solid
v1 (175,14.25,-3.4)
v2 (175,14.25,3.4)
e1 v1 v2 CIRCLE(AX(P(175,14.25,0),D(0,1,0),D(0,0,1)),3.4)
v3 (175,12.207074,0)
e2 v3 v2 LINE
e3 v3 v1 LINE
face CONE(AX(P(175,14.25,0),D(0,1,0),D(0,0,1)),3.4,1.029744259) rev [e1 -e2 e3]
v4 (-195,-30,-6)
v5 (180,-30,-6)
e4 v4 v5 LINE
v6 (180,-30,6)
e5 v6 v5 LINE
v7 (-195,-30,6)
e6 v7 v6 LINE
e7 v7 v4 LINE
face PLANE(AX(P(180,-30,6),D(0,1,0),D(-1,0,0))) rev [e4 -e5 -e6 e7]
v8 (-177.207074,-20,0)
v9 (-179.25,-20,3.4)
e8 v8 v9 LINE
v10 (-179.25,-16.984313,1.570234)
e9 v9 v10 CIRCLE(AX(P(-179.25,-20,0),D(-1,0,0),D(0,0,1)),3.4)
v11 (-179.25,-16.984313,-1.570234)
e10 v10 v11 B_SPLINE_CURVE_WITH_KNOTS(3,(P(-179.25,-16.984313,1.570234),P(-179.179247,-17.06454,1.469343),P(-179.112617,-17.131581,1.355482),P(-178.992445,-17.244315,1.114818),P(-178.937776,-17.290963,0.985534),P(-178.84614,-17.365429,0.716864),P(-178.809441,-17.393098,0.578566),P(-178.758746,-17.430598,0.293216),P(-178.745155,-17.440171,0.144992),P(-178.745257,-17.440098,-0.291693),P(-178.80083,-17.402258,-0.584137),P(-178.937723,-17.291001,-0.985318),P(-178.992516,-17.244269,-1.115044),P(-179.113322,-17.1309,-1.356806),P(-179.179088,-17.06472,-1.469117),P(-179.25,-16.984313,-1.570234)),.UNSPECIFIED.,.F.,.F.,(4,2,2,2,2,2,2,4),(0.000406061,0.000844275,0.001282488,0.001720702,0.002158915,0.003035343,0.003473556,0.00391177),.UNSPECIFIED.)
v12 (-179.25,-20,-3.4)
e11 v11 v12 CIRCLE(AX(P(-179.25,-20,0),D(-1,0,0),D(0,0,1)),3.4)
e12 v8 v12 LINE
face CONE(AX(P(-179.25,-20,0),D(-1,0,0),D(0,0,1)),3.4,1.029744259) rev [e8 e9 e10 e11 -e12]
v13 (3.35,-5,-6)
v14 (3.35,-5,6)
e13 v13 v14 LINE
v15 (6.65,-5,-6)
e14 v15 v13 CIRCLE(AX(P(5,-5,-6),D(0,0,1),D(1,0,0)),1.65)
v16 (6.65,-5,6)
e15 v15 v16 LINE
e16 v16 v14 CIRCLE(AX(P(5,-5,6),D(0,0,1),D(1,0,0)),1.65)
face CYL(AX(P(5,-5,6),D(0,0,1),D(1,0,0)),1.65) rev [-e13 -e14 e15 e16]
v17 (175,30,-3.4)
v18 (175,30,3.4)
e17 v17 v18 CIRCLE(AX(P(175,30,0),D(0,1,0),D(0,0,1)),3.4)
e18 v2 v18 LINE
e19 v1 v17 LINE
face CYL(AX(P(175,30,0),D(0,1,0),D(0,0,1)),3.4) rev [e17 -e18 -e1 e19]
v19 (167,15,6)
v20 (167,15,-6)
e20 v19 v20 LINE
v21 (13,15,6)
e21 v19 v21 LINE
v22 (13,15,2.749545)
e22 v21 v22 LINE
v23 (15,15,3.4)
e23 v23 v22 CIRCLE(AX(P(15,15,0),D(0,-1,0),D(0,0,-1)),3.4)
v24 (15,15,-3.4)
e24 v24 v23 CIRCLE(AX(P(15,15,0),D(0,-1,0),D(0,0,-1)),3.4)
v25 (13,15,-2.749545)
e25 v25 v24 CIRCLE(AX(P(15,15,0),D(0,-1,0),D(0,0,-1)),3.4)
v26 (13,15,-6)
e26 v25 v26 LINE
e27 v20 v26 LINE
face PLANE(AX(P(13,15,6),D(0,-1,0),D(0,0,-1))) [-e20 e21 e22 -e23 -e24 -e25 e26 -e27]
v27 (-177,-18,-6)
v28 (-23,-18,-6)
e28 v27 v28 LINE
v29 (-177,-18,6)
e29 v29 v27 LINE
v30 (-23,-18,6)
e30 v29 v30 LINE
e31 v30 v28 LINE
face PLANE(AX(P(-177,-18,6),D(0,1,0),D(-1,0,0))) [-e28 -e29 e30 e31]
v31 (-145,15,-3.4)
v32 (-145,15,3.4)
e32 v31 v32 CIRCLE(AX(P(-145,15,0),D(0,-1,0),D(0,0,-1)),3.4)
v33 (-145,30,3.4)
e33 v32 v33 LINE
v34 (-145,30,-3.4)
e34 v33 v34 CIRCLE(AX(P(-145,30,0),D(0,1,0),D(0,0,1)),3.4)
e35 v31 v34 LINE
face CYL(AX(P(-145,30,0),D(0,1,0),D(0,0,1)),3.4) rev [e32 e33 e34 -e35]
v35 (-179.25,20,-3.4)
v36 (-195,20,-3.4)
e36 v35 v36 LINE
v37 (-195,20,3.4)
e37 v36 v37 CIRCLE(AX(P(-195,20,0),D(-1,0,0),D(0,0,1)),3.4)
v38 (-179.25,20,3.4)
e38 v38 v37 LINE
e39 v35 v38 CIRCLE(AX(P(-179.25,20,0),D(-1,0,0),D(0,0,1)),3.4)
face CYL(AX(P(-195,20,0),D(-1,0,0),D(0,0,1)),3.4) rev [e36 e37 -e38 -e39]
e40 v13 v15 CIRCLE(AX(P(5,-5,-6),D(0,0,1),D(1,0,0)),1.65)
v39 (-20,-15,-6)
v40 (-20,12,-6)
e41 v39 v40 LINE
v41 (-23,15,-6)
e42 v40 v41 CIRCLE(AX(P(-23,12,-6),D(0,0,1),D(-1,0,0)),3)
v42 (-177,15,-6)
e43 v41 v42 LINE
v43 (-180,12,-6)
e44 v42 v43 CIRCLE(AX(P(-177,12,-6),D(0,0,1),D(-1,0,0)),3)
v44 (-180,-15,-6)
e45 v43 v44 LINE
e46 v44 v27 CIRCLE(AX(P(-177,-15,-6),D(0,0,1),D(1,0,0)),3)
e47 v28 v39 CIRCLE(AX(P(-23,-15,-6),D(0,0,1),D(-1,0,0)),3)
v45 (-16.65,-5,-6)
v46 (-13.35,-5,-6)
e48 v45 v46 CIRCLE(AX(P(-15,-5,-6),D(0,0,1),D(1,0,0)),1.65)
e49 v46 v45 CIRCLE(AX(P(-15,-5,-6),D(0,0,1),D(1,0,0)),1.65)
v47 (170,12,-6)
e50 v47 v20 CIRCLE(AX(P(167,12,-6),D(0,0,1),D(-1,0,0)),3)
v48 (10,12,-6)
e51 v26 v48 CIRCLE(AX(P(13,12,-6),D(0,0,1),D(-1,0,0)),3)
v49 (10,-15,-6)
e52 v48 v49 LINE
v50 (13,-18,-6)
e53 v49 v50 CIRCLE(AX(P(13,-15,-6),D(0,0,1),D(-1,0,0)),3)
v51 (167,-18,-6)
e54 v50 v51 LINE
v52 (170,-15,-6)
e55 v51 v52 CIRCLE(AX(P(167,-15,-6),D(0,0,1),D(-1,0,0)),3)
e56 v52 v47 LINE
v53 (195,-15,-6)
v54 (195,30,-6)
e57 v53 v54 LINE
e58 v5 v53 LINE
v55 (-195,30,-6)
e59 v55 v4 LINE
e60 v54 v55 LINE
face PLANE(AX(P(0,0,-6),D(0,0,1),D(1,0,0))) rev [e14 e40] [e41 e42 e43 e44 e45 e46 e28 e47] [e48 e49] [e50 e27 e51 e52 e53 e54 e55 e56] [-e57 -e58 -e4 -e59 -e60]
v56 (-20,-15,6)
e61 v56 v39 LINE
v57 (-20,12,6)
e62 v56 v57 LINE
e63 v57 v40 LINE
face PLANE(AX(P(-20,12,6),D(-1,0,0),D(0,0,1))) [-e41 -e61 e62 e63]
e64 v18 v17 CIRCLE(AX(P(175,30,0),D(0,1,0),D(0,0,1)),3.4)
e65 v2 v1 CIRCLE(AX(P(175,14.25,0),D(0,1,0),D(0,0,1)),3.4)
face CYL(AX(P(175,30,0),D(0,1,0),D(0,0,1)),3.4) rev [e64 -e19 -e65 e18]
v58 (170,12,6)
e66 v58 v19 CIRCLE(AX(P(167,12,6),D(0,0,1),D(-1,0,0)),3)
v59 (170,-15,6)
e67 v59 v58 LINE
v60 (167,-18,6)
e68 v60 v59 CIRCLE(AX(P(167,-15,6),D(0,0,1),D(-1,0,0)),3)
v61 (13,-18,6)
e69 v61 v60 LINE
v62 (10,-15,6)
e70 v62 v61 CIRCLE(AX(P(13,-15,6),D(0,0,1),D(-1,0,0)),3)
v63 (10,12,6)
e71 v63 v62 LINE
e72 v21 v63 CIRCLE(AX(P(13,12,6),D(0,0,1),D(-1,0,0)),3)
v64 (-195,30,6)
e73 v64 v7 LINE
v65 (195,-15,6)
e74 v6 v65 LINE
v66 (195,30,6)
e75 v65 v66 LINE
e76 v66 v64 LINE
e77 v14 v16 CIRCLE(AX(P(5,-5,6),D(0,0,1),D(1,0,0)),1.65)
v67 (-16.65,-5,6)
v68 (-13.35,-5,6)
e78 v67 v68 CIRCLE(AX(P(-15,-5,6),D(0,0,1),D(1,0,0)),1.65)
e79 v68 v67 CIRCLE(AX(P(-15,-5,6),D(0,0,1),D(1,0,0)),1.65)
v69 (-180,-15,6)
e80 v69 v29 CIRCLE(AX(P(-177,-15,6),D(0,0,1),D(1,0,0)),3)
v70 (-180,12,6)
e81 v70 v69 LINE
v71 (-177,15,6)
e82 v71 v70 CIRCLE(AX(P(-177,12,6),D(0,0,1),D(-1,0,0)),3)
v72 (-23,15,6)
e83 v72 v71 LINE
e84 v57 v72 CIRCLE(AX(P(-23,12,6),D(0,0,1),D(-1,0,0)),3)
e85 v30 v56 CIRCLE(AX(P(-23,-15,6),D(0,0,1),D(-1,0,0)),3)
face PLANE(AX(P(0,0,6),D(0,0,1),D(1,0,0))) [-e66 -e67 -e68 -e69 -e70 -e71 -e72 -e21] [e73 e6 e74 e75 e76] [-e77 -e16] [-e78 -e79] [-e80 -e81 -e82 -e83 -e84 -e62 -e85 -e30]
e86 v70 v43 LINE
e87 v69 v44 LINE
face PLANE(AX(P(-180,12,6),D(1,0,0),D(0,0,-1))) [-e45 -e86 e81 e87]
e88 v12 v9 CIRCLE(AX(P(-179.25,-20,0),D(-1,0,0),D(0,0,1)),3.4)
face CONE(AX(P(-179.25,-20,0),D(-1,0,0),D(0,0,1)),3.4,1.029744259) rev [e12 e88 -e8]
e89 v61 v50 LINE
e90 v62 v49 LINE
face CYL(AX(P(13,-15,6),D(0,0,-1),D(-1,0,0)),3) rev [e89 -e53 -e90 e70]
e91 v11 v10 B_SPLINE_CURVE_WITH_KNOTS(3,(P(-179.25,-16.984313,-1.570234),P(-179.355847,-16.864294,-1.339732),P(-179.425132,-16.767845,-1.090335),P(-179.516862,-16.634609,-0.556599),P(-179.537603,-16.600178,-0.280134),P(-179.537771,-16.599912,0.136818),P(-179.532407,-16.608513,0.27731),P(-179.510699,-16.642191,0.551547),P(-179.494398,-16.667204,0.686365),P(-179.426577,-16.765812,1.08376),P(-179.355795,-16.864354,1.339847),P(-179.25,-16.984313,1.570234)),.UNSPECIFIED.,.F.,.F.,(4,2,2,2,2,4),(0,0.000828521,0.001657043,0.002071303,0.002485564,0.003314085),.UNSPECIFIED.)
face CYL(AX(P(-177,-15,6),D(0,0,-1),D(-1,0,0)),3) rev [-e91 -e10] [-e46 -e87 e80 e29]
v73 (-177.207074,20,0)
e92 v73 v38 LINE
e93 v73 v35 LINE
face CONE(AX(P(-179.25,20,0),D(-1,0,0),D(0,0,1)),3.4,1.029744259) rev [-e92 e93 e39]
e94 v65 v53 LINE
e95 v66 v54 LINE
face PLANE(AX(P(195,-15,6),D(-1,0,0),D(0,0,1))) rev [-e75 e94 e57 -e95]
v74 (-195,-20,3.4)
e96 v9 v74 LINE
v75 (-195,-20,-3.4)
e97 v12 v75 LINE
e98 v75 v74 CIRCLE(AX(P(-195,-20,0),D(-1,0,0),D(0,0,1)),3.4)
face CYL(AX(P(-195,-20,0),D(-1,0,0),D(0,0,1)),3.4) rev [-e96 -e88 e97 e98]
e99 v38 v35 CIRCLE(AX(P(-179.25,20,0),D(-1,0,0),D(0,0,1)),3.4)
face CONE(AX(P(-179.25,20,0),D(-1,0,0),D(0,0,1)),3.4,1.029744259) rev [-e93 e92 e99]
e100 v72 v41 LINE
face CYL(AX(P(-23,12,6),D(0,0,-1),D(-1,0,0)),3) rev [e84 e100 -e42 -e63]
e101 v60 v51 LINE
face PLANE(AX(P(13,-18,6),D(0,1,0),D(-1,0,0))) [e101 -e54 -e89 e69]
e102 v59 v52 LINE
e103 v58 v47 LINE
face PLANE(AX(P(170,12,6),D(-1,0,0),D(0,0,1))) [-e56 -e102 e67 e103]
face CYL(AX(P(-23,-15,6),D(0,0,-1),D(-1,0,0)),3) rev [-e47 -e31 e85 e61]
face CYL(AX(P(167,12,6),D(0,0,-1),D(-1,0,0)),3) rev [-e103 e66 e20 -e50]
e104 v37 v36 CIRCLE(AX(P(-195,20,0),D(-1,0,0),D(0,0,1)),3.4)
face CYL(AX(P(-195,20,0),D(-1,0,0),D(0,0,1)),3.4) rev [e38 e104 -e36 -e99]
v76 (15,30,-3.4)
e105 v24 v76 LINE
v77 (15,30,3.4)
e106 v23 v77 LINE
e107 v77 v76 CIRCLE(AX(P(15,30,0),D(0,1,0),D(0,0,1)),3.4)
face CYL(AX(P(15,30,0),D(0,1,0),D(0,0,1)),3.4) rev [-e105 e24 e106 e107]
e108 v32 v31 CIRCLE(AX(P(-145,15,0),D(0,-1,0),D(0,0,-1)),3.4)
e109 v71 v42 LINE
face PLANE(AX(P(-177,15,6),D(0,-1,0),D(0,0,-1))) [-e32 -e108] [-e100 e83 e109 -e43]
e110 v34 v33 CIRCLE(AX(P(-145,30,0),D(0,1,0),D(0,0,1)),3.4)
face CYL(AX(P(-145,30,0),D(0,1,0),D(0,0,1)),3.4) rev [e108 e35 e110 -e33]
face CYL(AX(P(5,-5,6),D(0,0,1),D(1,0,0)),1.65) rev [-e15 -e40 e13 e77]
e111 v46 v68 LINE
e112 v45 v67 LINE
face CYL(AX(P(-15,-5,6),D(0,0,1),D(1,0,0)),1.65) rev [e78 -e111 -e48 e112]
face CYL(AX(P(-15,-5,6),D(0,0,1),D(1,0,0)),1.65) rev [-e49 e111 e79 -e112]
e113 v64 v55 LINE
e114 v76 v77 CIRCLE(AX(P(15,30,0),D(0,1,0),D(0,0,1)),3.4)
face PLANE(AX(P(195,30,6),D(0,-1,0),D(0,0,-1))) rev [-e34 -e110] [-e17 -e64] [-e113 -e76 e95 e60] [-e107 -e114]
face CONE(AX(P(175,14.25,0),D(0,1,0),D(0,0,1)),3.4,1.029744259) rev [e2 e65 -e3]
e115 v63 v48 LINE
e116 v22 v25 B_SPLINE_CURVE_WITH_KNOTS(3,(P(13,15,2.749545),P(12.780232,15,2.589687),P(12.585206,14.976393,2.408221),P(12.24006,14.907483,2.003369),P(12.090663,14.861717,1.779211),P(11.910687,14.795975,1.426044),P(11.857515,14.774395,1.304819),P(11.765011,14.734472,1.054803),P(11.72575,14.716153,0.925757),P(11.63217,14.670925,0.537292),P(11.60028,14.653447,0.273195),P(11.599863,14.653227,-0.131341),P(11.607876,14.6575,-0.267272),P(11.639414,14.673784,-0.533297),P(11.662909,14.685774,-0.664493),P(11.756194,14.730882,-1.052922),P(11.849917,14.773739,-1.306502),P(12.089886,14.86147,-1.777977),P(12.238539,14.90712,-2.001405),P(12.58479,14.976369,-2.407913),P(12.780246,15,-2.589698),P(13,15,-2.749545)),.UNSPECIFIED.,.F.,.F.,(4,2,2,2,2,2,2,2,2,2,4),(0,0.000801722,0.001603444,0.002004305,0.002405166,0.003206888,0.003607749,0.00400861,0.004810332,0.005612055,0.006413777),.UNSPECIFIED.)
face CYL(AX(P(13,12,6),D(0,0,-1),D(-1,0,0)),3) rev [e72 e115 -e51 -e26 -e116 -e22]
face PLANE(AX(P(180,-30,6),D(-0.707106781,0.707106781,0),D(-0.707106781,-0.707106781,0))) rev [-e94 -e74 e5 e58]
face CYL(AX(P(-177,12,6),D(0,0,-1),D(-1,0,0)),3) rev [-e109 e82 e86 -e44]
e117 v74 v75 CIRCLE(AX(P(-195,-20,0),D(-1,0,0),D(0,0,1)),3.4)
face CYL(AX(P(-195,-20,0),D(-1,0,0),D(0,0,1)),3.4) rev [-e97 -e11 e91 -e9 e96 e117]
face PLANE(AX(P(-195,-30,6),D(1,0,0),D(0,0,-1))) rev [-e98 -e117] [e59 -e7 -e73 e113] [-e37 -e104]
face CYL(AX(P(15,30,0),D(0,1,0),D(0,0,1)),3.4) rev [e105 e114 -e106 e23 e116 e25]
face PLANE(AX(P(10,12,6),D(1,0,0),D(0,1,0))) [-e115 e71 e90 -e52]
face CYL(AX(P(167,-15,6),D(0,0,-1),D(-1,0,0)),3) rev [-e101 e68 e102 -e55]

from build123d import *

# Parameters (mm, degrees)
EXTRUDE_1_DEPTH        = 6
HOLE_WIZARD_M8_1_D     = 6.8
HOLE_WIZARD_M8_1_DEPTH = 15.75
HOLE_WIZARD_M8_1_TIP   = 2.042926105
HOLE_WIZARD_M4_1_D     = 3.3
PATTERN_LINEAR_1_COUNT = 3
PATTERN_LINEAR_1_PITCH = 160


with BuildPart() as part:
    # 草图1 → 凸台-拉伸1 (new, symmetric)
    with BuildSketch(Plane.XY):
        Polygon((180, -30), (195, -15), (195, 30), (-195, 30), (-195, -30), align=None)
        with BuildLine():
            Line((-177, 15), (-23, 15))
            ThreePointArc((-23, 15), (-20.878679656, 14.121320344), (-20, 12))
            Line((-20, 12), (-20, -15))
            ThreePointArc((-20, -15), (-20.878679656, -17.121320344), (-23, -18))
            Line((-23, -18), (-177, -18))
            ThreePointArc((-177, -18), (-179.121320344, -17.121320344), (-180, -15))
            Line((-180, -15), (-180, 12))
            ThreePointArc((-180, 12), (-179.121320344, 14.121320344), (-177, 15))
        make_face(mode=Mode.SUBTRACT)
        with BuildLine():
            Line((13, 15), (167, 15))
            ThreePointArc((167, 15), (169.121320344, 14.121320344), (170, 12))
            Line((170, 12), (170, -15))
            ThreePointArc((170, -15), (169.121320344, -17.121320344), (167, -18))
            Line((167, -18), (13, -18))
            ThreePointArc((13, -18), (10.878679656, -17.121320344), (10, -15))
            Line((10, -15), (10, 12))
            ThreePointArc((10, 12), (10.878679656, 14.121320344), (13, 15))
        make_face(mode=Mode.SUBTRACT)
    extrude(amount=EXTRUDE_1_DEPTH, both=True)

    # M8 螺纹孔1
    with Locations(Plane(origin=(-195, 20, 0), x_dir=(0, 0, -1), z_dir=(-1, 0, 0))):
        with Locations((0, 0), (0, 40)):
            Hole(HOLE_WIZARD_M8_1_D / 2, depth=HOLE_WIZARD_M8_1_DEPTH)
            with Locations((0, 0, -(HOLE_WIZARD_M8_1_DEPTH + HOLE_WIZARD_M8_1_TIP / 2))):  # 118° drill point
                Cone(0, HOLE_WIZARD_M8_1_D / 2, HOLE_WIZARD_M8_1_TIP, mode=Mode.SUBTRACT)

    # M4 螺纹孔1 (through all)
    with Locations(Plane.XY.offset(6)):
        with Locations((-15, -5), (5, -5)):
            Hole(HOLE_WIZARD_M4_1_D / 2)

    # 草图6 → M8 螺纹孔2 (revolve, cut)
    with BuildSketch(Plane(origin=(-145, 30, 0), x_dir=(0, 0, 1), z_dir=(1, 0, 0))):
        Polygon((0, 0), (0, 17.792926105), (3.4, 15.75), (3.4, 0), align=None)
    hole_wizard_m8_2 = revolve(axis=Axis((-145, 36.35, 0), (0, -1, 0)), mode=Mode.SUBTRACT)

    # 阵列(线性)1: M8 螺纹孔2 ×3
    with Locations(*[(i * PATTERN_LINEAR_1_PITCH, 0, 0) for i in range(1, PATTERN_LINEAR_1_COUNT)]):
        add(hole_wizard_m8_2, mode=Mode.SUBTRACT)


solid = part.part
